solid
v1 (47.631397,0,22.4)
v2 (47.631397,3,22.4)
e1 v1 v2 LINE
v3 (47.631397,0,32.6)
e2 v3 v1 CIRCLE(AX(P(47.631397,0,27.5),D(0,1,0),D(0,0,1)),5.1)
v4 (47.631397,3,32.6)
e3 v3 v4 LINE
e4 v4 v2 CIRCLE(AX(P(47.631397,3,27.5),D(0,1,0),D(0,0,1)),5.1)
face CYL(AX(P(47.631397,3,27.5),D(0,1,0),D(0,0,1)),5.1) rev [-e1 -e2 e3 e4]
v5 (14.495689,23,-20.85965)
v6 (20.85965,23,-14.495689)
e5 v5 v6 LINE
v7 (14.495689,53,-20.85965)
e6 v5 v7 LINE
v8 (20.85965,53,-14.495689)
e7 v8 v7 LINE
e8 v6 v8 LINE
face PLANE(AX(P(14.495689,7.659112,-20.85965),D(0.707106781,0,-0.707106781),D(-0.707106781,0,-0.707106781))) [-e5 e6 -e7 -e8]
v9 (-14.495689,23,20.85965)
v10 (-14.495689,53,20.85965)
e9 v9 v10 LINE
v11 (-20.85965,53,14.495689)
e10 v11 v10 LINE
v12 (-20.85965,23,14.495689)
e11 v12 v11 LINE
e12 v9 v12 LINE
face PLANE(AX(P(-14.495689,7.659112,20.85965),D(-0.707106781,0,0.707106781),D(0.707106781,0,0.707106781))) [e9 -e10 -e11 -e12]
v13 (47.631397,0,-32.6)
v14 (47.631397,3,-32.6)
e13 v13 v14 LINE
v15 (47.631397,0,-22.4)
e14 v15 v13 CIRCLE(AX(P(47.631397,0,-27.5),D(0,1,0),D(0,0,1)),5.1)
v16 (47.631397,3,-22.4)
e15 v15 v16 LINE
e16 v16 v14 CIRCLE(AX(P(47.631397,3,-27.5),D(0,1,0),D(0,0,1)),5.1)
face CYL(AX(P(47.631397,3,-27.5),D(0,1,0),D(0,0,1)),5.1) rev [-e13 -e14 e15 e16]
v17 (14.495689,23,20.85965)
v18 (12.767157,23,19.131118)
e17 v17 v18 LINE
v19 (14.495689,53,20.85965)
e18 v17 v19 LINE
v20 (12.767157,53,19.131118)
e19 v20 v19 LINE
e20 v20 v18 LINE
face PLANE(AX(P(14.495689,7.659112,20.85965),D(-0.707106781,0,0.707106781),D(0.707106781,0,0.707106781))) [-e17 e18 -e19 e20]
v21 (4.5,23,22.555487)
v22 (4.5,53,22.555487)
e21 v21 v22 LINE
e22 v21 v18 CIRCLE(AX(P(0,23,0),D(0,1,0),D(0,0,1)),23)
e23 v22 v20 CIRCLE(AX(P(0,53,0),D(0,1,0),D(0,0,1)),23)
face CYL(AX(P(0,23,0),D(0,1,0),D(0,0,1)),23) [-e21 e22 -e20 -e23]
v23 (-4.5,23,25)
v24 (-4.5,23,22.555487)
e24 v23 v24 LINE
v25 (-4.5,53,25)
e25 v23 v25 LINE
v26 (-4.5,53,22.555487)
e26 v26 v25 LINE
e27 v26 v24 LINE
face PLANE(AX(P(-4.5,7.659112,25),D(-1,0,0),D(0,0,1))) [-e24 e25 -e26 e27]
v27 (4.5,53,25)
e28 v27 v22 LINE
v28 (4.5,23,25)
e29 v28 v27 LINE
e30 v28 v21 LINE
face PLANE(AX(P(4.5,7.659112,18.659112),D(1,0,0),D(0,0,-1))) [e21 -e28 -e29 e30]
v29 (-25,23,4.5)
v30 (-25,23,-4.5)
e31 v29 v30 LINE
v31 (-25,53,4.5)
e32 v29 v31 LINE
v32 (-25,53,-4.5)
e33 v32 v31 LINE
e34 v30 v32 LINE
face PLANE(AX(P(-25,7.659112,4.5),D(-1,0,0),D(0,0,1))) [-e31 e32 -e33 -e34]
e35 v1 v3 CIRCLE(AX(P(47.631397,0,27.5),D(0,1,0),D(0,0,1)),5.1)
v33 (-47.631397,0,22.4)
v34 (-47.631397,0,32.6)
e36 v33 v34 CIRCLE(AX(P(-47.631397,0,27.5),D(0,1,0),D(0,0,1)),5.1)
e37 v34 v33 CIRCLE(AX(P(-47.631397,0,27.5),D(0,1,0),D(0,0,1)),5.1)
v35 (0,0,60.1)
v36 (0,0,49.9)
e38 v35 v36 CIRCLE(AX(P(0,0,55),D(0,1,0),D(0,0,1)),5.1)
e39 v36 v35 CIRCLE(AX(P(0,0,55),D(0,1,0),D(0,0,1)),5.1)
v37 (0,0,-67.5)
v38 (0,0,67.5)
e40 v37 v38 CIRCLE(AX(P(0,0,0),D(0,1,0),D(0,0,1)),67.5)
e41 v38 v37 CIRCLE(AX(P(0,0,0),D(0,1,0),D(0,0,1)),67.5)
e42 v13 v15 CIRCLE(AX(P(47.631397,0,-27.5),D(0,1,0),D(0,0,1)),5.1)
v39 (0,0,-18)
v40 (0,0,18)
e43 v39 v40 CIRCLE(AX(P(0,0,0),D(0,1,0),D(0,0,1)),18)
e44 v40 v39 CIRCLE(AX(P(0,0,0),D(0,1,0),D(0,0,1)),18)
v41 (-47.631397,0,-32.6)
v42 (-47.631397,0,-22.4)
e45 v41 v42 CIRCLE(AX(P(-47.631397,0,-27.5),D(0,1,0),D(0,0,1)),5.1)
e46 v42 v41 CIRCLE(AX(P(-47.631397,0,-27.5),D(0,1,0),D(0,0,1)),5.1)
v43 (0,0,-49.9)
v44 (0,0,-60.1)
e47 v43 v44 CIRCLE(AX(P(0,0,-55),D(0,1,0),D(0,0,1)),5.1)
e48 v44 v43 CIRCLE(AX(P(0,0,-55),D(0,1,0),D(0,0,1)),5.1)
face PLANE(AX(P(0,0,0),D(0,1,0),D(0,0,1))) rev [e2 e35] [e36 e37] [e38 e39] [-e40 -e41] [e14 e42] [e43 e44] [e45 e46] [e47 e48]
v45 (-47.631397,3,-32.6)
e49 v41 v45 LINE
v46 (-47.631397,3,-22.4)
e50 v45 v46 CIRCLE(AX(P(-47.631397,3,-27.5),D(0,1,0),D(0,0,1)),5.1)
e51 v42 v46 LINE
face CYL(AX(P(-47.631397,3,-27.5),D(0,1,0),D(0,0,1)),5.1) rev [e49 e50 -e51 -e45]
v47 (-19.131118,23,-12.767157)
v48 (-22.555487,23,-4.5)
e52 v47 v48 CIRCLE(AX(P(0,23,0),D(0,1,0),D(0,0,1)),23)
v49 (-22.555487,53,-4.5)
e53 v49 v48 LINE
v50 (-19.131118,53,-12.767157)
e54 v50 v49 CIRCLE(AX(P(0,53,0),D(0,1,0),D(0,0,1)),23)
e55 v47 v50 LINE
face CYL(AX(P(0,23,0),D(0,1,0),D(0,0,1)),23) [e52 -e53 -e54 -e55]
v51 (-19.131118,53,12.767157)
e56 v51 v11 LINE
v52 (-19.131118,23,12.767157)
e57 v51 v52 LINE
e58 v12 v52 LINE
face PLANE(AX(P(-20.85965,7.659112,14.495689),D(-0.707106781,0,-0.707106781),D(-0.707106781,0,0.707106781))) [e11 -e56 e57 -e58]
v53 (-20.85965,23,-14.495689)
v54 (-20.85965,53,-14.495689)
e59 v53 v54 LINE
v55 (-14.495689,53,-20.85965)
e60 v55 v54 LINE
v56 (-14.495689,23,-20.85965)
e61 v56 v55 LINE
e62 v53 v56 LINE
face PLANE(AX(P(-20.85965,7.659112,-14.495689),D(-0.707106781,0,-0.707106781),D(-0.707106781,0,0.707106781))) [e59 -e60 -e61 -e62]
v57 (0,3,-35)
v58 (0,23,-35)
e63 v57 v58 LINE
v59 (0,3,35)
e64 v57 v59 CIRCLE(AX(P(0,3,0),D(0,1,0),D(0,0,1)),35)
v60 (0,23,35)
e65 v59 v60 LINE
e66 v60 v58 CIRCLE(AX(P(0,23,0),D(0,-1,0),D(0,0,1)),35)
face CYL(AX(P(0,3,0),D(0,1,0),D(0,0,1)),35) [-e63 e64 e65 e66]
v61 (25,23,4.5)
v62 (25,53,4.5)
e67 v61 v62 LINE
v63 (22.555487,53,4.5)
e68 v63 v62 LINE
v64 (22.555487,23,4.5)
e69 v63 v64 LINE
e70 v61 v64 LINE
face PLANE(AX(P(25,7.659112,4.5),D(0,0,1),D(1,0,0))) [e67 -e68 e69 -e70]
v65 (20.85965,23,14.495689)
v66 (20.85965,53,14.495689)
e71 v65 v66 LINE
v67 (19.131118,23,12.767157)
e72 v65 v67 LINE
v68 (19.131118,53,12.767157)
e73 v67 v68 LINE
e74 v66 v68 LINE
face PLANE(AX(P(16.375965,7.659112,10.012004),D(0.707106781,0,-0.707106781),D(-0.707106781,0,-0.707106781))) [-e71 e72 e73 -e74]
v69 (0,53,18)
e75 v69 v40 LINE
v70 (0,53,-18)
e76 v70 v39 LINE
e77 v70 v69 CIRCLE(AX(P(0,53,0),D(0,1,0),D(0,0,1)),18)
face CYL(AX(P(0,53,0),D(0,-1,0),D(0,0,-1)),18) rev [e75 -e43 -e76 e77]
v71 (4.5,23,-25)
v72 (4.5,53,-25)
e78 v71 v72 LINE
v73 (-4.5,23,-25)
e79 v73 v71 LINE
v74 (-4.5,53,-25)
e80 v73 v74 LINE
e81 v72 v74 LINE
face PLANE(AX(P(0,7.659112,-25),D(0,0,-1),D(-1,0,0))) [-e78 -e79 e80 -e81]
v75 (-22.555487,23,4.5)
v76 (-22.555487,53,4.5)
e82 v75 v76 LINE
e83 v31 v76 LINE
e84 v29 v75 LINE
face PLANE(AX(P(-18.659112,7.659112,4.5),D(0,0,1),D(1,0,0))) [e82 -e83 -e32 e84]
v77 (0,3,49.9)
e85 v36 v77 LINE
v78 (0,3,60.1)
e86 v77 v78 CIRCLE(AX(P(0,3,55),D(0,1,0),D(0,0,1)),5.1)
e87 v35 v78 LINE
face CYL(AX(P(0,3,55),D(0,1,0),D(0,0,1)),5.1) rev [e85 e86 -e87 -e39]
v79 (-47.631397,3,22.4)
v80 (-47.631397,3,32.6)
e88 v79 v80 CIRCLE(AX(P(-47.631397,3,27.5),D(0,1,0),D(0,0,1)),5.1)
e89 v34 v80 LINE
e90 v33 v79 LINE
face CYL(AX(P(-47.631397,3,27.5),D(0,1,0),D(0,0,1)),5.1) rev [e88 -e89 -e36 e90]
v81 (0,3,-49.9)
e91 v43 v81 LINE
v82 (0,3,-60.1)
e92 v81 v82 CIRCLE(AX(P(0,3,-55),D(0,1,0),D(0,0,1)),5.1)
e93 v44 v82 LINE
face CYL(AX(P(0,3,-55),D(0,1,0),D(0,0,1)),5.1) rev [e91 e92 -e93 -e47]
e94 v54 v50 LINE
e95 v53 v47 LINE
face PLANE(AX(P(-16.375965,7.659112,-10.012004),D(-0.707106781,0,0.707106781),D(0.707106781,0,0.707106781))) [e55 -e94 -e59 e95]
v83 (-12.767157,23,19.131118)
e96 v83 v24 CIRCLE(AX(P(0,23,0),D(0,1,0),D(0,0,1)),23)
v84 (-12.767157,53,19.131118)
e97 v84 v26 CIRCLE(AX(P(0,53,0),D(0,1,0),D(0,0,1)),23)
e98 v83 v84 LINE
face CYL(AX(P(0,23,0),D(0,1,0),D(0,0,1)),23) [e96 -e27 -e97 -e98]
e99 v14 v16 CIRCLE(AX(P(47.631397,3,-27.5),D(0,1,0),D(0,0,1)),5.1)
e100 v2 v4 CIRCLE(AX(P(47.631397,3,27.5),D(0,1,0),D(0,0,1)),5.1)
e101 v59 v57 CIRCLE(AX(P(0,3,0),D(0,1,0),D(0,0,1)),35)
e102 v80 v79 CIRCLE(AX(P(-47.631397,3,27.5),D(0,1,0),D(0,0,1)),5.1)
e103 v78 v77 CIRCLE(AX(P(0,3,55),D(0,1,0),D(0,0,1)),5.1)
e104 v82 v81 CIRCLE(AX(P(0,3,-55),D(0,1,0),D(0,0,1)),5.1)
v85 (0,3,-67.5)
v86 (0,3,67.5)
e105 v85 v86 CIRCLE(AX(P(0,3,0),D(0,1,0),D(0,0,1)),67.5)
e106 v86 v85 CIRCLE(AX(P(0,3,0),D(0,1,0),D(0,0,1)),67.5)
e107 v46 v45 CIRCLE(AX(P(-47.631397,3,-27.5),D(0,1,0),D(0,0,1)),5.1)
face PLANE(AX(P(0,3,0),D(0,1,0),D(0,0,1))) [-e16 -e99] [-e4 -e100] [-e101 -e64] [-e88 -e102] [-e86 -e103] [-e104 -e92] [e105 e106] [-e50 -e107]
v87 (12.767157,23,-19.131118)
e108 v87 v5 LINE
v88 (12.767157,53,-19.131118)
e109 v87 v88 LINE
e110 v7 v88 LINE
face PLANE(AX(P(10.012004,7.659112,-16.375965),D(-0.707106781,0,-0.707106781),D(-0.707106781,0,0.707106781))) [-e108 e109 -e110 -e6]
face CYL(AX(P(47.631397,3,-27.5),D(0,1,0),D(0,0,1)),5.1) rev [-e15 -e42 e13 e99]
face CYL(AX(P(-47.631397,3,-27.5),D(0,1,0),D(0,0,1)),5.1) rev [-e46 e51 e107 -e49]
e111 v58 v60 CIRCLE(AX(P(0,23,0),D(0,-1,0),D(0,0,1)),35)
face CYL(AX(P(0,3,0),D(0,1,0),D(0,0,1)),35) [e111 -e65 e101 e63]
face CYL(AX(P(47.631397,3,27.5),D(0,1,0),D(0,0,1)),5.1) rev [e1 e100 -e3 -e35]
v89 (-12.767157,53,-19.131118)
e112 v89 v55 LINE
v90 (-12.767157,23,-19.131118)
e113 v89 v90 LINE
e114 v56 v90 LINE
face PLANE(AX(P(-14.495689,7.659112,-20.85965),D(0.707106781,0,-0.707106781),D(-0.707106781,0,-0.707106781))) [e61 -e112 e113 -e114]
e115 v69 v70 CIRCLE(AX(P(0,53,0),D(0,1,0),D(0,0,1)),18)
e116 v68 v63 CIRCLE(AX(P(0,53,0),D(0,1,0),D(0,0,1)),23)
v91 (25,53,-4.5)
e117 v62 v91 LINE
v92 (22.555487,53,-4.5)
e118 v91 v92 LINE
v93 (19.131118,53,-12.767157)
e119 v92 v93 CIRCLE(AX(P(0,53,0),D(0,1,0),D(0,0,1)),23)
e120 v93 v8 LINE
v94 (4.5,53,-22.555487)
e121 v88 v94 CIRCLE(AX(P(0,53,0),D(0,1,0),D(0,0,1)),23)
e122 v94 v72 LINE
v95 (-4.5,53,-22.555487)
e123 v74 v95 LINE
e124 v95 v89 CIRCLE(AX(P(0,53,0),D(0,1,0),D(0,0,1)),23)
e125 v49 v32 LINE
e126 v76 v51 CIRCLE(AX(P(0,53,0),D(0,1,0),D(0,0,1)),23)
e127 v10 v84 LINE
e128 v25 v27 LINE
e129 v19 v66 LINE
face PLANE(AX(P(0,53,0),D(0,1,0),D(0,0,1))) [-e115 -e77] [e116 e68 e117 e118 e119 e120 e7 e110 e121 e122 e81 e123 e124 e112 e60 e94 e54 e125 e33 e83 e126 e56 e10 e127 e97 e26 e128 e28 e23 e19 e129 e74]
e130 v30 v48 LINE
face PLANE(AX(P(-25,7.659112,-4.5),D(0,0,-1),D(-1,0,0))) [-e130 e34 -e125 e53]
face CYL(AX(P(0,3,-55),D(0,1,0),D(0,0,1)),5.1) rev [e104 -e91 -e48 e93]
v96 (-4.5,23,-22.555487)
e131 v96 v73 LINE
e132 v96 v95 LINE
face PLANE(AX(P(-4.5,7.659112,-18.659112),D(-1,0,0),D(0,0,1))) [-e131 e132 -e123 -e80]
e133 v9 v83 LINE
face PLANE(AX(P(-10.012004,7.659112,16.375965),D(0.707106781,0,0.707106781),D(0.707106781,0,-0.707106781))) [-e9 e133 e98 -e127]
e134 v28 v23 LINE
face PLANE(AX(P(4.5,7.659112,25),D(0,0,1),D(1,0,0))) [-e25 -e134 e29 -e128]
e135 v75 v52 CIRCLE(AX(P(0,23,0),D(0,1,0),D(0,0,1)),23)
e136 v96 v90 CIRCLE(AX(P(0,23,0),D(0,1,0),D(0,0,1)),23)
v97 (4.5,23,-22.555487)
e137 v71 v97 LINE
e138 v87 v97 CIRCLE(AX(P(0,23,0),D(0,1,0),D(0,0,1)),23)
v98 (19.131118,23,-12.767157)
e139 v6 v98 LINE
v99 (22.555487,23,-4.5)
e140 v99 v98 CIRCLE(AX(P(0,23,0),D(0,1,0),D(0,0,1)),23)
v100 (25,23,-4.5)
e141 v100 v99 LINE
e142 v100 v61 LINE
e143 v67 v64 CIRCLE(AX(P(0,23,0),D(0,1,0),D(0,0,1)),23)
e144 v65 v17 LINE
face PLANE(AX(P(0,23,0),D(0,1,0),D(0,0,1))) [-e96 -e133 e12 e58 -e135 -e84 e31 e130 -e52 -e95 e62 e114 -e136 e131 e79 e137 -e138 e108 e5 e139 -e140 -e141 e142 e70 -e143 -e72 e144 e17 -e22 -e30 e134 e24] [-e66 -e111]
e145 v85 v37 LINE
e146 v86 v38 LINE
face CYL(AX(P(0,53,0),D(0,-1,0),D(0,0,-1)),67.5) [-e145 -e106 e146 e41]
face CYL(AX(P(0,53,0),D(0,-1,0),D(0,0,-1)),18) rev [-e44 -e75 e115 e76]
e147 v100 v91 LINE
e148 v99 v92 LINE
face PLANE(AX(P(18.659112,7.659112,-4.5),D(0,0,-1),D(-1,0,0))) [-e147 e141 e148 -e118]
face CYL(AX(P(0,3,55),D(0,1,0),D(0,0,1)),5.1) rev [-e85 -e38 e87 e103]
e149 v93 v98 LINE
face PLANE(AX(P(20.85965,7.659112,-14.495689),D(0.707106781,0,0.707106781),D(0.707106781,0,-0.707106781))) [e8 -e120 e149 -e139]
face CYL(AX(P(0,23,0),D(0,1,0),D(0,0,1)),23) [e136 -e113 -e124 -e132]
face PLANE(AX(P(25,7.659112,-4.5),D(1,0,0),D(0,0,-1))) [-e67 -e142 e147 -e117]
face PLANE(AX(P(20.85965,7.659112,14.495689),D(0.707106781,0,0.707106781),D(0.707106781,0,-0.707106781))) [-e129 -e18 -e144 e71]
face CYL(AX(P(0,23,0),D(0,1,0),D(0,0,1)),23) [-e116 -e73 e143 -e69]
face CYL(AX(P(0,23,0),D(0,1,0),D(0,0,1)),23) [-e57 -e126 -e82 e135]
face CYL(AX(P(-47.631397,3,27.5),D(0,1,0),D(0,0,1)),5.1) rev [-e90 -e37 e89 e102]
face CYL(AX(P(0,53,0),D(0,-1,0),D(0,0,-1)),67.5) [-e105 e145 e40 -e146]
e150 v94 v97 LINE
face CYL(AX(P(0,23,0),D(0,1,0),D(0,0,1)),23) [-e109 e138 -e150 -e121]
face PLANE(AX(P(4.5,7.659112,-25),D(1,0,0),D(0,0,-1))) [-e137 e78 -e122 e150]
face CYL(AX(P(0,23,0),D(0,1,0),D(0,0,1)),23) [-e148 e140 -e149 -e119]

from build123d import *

# Parameters (mm, degrees)
SKETCH_1_R              = 67.5
SKETCH_1_R_2            = 18
EXTRUDE_1_DEPTH         = 53
SKETCH_2_OUTSIDE_W      = 176.628
SKETCH_2_OUTSIDE_H      = 176.628
SKETCH_2_OUTSIDE_R      = 35
CUT_EXTRUDE_1_DEPTH     = 50
SKETCH_3_OUTSIDE_W      = 176.628
SKETCH_3_OUTSIDE_H      = 176.628
SKETCH_3_OUTSIDE_R      = 23
CUT_EXTRUDE_2_DEPTH     = 30
EXTRUDE_2_DEPTH         = 30
HOLE_WIZARD_M12_1_D     = 10.2
HOLE_WIZARD_M12_1_DEPTH = 5
HOLE_WIZARD_M12_1_TIP   = 3.064389157


with BuildPart() as part:
    # 草图1 → 凸台-拉伸1 (new body)
    with BuildSketch(Plane(origin=(0, 0, 0), x_dir=(1, 0, 0), z_dir=(0, 1, 0))):
        with Locations(Location((0, 0, 0), (0, 0, 270))):
            Circle(SKETCH_1_R)
        with Locations(Location((0, 0, 0), (0, 0, 270))):
            Circle(SKETCH_1_R_2, mode=Mode.SUBTRACT)
    extrude(amount=EXTRUDE_1_DEPTH)

    # 草图2 outside → 切除-拉伸1 (cut)
    with BuildSketch(Plane(origin=(0, 53, 0), x_dir=(1, 0, 0), z_dir=(0, 1, 0))):
        Rectangle(SKETCH_2_OUTSIDE_W, SKETCH_2_OUTSIDE_H)
        with Locations(Location((0, 0, 0), (0, 0, 270))):
            Circle(SKETCH_2_OUTSIDE_R, mode=Mode.SUBTRACT)
    extrude(amount=-CUT_EXTRUDE_1_DEPTH, mode=Mode.SUBTRACT)

    # 草图3 outside → 切除-拉伸2 (cut)
    with BuildSketch(Plane(origin=(0, 53, 0), x_dir=(1, 0, 0), z_dir=(0, 1, 0))):
        Rectangle(SKETCH_3_OUTSIDE_W, SKETCH_3_OUTSIDE_H)
        with Locations(Location((0, 0, 0), (0, 0, 270))):
            Circle(SKETCH_3_OUTSIDE_R, mode=Mode.SUBTRACT)
    extrude(amount=-CUT_EXTRUDE_2_DEPTH, mode=Mode.SUBTRACT)

    # 草图4 → 凸台-拉伸2 (add)
    with BuildSketch(Plane(origin=(0, 53, 0), x_dir=(1, 0, 0), z_dir=(0, 1, 0))):
        Polygon((0, 25), (4.5, 25), (4.5, 18.659112383), (-4.5, 18.659112383), (-4.5, 25), align=None)
        Polygon((10.012004382, 16.375965412), (14.495689014, 20.859650045), (17.67766953, 17.67766953), (20.859650045, 14.495689014), (16.375965412, 10.012004382), align=None)
        Polygon((18.659112383, 4.5), (25, 4.5), (25, 0), (25, -4.5), (18.659112383, -4.5), align=None)
        Polygon((16.375965412, -10.012004382), (20.859650045, -14.495689014), (17.67766953, -17.67766953), (14.495689014, -20.859650045), (10.012004382, -16.375965412), align=None)
        Polygon((4.5, -18.659112383), (4.5, -25), (0, -25), (-4.5, -25), (-4.5, -18.659112383), align=None)
        Polygon((-10.012004382, -16.375965412), (-14.495689014, -20.859650045), (-17.67766953, -17.67766953), (-20.859650045, -14.495689014), (-16.375965412, -10.012004382), align=None)
        Polygon((-18.659112383, -4.5), (-25, -4.5), (-25, 0), (-25, 4.5), (-18.659112383, 4.5), align=None)
        Polygon((-16.375965412, 10.012004382), (-20.859650045, 14.495689014), (-17.67766953, 17.67766953), (-14.495689014, 20.859650045), (-10.012004382, 16.375965412), align=None)
    extrude(amount=-EXTRUDE_2_DEPTH)

    # M12 螺纹孔的螺纹孔钻头1
    with Locations(Plane(origin=(0, 3, 0), x_dir=(1, 0, 0), z_dir=(0, 1, 0))):
        with Locations((0, 55), (-47.631397208, 27.5), (-47.631397208, -27.5), (0, -55), (47.631397208, -27.5), (47.631397208, 27.5)):
            Hole(HOLE_WIZARD_M12_1_D / 2, depth=HOLE_WIZARD_M12_1_DEPTH)
            with Locations((0, 0, -(HOLE_WIZARD_M12_1_DEPTH + HOLE_WIZARD_M12_1_TIP / 2))):  # 118° drill point
                Cone(0, HOLE_WIZARD_M12_1_D / 2, HOLE_WIZARD_M12_1_TIP, mode=Mode.SUBTRACT)


solid = part.part
